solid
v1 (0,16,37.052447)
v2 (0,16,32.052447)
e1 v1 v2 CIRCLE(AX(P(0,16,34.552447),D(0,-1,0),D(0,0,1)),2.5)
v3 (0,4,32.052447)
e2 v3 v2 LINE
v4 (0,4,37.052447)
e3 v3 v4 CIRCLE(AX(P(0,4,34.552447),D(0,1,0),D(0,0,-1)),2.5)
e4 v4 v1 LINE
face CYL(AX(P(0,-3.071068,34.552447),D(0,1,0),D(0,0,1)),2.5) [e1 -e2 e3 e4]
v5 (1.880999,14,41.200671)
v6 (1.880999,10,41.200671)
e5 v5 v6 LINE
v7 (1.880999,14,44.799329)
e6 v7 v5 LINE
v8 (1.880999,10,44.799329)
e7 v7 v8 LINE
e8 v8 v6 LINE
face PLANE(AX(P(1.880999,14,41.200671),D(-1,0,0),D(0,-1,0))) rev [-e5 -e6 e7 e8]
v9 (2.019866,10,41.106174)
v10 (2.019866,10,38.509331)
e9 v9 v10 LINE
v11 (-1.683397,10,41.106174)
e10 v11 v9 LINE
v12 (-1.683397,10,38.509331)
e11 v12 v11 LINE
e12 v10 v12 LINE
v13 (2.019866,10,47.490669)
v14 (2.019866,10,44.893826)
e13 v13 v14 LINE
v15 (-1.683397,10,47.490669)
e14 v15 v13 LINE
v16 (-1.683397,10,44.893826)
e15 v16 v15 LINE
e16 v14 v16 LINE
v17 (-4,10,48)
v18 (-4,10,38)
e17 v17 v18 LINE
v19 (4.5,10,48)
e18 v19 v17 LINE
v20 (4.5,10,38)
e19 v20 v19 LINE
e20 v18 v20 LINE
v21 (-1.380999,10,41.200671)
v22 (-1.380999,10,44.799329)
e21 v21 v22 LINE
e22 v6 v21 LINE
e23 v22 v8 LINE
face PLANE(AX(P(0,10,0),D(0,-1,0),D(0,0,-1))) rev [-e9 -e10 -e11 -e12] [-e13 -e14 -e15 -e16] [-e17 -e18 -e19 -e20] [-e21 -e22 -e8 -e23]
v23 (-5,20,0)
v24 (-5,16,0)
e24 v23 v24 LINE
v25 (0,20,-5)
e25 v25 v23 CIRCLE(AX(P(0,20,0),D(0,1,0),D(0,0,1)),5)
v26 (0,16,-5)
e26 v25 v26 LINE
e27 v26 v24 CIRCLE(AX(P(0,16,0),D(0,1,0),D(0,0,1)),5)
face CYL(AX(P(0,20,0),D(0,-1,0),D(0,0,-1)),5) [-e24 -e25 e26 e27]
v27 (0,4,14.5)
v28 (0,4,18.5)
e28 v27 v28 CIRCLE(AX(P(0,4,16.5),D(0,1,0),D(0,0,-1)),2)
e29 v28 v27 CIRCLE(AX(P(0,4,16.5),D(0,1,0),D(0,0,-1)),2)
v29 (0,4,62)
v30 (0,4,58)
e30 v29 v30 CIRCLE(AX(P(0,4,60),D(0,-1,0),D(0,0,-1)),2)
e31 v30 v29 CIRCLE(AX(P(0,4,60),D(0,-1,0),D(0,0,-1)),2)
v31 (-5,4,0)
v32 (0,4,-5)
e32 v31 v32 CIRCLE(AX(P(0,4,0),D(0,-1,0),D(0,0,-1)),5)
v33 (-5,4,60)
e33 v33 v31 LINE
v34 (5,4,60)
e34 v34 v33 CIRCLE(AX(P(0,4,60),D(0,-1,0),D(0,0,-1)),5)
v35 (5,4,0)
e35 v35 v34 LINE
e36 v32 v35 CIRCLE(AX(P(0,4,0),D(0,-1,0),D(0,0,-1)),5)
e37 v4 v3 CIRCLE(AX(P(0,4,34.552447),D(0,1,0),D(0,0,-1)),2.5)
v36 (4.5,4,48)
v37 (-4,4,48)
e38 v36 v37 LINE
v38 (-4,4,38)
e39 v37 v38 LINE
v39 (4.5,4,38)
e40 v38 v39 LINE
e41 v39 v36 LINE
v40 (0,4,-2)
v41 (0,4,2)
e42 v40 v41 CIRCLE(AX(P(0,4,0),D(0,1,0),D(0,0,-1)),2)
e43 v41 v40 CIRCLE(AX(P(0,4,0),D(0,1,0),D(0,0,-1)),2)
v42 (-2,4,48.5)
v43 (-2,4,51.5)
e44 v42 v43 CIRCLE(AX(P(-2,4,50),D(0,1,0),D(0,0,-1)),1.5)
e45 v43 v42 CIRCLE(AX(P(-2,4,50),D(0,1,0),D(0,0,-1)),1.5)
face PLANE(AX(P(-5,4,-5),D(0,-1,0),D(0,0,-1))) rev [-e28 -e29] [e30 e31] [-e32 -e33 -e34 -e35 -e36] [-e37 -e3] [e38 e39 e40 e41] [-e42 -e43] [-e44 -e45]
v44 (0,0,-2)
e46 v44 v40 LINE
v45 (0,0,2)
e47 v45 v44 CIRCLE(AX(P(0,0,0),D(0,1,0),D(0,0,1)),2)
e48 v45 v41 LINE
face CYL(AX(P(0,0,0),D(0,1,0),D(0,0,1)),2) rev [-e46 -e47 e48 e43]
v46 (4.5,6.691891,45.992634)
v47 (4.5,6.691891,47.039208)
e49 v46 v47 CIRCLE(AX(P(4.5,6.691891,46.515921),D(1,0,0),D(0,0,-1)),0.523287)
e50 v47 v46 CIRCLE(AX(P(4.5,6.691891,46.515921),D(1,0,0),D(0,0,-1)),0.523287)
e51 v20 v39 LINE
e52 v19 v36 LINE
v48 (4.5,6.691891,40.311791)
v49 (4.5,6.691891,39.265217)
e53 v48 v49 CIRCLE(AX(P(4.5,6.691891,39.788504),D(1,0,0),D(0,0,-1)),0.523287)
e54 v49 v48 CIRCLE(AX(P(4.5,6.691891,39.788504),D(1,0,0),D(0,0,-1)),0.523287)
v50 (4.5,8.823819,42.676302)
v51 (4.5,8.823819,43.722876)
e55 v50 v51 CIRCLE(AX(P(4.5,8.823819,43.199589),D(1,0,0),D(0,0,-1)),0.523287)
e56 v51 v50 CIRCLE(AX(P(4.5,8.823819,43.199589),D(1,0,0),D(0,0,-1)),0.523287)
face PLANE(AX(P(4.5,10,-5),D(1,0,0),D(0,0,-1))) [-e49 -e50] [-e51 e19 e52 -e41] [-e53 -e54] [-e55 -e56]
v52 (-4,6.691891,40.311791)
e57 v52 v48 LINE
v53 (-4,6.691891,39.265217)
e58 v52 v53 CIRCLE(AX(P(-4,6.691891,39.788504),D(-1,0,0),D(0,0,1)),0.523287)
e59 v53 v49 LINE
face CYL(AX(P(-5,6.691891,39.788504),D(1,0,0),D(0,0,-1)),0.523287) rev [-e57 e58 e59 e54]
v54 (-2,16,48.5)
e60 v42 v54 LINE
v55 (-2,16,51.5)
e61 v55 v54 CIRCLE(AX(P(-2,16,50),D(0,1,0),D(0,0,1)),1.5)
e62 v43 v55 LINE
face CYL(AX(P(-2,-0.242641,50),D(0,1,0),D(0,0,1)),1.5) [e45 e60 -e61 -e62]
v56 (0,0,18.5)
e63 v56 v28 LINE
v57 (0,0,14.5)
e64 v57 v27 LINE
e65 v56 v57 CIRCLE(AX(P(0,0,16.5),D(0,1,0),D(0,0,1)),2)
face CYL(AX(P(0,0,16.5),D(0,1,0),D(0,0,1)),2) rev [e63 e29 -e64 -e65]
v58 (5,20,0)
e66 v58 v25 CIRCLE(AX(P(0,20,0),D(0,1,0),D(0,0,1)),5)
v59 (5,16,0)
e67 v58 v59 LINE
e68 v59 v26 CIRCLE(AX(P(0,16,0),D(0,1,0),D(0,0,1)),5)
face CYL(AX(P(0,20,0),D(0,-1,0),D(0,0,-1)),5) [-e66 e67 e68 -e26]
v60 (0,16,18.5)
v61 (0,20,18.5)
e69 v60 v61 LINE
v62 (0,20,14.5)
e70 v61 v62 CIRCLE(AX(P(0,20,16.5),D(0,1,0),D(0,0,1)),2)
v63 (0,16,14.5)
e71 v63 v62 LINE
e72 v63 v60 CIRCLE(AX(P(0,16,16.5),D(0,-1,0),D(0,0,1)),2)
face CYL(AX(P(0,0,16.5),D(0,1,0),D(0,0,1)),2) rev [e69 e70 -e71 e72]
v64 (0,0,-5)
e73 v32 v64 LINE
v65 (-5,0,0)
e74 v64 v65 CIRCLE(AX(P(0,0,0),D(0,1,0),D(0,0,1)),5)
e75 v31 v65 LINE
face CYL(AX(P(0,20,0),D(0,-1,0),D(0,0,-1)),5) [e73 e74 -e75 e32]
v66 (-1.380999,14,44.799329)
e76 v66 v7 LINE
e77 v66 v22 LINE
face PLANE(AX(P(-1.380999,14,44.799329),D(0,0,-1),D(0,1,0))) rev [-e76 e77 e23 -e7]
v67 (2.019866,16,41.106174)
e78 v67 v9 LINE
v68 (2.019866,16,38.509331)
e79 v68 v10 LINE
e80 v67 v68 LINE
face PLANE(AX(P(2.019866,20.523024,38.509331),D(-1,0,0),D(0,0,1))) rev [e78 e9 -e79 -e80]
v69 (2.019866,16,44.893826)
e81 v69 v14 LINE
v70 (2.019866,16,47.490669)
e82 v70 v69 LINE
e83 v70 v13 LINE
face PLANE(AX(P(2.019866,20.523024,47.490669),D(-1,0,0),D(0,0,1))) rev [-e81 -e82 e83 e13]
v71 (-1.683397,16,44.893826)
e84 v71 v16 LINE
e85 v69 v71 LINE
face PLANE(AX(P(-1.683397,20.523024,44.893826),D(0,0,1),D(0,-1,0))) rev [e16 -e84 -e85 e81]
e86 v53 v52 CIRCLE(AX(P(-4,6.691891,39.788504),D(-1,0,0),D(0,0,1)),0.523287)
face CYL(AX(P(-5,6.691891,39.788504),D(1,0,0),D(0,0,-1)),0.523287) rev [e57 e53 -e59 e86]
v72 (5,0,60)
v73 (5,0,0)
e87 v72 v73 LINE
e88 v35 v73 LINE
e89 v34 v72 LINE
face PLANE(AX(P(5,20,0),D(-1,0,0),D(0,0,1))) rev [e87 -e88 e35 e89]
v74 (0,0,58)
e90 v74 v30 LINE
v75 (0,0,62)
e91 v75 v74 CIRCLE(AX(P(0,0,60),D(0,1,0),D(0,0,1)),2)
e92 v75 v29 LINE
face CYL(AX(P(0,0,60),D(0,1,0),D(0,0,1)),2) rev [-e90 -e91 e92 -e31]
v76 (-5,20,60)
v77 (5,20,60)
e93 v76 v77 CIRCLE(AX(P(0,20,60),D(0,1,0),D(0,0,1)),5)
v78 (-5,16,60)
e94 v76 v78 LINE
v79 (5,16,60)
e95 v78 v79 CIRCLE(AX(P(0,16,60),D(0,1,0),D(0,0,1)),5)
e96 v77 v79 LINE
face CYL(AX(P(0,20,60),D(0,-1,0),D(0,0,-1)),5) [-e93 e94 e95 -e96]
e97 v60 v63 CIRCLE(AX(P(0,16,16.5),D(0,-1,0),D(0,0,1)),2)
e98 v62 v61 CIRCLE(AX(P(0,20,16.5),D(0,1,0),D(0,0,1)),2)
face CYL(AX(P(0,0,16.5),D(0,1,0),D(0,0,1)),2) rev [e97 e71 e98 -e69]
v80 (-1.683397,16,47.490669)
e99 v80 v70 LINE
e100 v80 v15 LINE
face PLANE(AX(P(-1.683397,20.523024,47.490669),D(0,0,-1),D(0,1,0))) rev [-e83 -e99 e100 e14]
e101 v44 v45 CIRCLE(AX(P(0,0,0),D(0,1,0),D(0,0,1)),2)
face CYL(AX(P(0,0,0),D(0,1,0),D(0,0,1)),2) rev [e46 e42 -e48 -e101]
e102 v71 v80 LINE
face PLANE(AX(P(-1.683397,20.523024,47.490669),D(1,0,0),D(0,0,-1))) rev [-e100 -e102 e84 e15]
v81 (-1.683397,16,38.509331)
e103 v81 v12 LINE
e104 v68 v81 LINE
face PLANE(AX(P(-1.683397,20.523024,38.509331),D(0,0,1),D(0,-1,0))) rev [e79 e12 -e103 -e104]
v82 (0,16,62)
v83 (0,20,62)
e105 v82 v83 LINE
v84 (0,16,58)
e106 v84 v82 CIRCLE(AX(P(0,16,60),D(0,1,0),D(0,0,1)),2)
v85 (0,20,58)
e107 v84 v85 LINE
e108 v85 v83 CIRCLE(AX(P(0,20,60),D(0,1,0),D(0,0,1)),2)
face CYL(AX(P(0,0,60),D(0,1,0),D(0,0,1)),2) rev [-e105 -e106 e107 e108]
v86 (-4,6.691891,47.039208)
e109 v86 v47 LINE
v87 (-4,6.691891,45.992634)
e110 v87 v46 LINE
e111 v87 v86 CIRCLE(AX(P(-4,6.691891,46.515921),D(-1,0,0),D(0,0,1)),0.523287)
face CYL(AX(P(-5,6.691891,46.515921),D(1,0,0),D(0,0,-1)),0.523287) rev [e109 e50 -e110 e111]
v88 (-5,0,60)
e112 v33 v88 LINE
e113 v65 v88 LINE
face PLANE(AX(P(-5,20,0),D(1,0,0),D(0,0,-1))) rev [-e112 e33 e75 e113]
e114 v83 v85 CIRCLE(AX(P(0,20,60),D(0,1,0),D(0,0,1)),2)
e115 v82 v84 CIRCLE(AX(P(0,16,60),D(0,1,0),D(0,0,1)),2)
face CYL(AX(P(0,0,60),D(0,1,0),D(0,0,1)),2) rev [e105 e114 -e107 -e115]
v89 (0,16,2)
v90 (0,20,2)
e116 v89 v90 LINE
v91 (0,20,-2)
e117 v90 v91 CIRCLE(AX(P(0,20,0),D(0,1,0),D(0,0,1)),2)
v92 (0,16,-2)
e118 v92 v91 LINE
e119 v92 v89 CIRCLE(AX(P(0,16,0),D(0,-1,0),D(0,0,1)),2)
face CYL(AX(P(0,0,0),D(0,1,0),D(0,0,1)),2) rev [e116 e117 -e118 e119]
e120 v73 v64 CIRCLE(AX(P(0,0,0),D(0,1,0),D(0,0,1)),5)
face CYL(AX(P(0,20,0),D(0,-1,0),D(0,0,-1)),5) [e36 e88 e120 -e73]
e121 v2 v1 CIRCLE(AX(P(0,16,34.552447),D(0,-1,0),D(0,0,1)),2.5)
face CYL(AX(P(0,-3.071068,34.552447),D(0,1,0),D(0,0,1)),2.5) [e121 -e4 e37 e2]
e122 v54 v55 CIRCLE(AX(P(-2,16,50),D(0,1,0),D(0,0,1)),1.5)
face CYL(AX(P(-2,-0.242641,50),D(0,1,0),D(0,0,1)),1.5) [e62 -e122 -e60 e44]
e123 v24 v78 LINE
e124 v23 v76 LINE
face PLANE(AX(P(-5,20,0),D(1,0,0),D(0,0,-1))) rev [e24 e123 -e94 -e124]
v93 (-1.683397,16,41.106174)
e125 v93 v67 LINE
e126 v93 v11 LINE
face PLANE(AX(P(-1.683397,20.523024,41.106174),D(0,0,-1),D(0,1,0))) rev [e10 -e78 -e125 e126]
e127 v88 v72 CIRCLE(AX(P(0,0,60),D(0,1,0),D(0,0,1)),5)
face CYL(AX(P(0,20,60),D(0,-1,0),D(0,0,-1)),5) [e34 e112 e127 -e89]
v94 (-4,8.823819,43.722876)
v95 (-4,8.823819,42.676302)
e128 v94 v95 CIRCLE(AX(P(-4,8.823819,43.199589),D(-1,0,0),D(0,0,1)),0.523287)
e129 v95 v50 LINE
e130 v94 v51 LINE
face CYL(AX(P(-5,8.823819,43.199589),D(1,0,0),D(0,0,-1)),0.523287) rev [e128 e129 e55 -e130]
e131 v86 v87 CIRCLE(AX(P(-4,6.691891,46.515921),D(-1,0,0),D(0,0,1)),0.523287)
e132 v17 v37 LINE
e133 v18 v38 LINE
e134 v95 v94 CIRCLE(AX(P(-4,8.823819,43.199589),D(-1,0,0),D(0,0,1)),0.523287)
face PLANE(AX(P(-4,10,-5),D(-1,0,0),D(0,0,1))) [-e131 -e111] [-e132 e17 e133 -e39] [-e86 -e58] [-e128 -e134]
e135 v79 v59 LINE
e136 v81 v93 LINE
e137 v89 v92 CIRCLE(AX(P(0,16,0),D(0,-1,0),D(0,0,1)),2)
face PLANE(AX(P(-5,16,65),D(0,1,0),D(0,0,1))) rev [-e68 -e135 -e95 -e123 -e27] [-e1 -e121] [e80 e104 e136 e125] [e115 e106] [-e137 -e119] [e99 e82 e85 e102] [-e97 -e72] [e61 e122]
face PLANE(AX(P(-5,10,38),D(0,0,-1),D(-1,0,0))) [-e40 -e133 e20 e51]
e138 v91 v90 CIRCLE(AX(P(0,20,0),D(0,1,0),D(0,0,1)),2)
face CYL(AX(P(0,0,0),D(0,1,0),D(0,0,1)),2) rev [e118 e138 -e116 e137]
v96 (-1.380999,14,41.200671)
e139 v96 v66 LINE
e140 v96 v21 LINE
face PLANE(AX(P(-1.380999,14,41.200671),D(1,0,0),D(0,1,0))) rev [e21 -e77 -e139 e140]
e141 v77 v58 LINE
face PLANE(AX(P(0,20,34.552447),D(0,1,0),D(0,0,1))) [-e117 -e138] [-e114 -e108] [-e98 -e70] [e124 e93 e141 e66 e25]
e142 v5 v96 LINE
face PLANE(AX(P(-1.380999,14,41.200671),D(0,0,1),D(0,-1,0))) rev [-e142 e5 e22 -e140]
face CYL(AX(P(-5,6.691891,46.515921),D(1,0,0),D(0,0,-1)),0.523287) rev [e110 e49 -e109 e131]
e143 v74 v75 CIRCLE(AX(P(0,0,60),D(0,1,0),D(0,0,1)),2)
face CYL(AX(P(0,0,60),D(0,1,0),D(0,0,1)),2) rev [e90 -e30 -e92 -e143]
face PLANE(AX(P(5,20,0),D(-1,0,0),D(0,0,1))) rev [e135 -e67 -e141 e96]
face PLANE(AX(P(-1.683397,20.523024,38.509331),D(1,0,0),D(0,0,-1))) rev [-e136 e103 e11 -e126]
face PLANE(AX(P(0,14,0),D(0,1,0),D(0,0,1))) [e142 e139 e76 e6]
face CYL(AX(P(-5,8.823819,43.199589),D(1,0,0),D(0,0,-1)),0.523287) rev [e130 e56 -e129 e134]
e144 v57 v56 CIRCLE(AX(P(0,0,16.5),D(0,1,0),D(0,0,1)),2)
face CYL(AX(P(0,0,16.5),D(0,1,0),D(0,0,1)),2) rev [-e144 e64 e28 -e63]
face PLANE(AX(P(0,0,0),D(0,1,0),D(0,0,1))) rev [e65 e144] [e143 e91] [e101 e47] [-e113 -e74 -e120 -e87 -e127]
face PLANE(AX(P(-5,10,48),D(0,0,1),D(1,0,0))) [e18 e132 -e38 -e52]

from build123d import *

# Parameters (mm, degrees)
BOSS_EXTRUDE1_DEPTH     = 20
SKETCH2_R               = 2
CUT_EXTRUDE1_DEPTH      = 69.190908485
CUT_EXTRUDE2_DEPTH      = 69.738635424
CUT_EXTRUDE2_DEPTH_BACK = 69.738635424
SKETCH3_W               = 70
SKETCH3_H               = 12
CUT_EXTRUDE3_DEPTH      = 69.190908485
CUT_EXTRUDE3_DEPTH_BACK = 69.190908485
SKETCH4_R               = 2
SKETCH5_R               = 2.5
BOSS_EXTRUDE2_DEPTH     = 16
SKETCH6_R               = 1.5
BOSS_EXTRUDE3_DEPTH     = 16
BOSS_EXTRUDE4_START     = -16
BOSS_EXTRUDE4_DEPTH     = 6
CUT_EXTRUDE4_DEPTH      = 69.667677986
CUT_EXTRUDE4_DEPTH_BACK = 69.667677986
SKETCH8_R               = 0.52328701
SKETCH9_W               = 3.261997226
SKETCH9_H               = 3.598658034
BOSS_EXTRUDE5_DEPTH     = 4
SKETCH10_W              = 3.703262865
SKETCH10_H              = 2.596843015
BOSS_EXTRUDE6_DEPTH     = 6


with BuildPart() as part:
    # Sketch1 → Boss-Extrude1 (new body)
    with BuildSketch(Plane(origin=(0, 0, 0), x_dir=(1, 0, 0), z_dir=(0, 1, 0))):
        with BuildLine():
            Line((-5, 0), (-5, -60))
            ThreePointArc((-5, -60), (0, -65), (5, -60))
            Line((5, -60), (5, 0))
            ThreePointArc((5, 0), (0, 5), (-5, 0))
        make_face()
    extrude(amount=BOSS_EXTRUDE1_DEPTH)

    # Sketch2 → Cut-Extrude1 (cut, through all)
    with BuildSketch(Plane(origin=(0, 20, 0), x_dir=(1, 0, 0), z_dir=(0, 1, 0))):
        with Locations(Location((0, 0, 0), (0, 0, 270))):
            Circle(SKETCH2_R)
        with Locations(Location((0, -16.5, 0), (0, 0, 270))):
            Circle(SKETCH2_R)
    extrude(amount=-CUT_EXTRUDE1_DEPTH, mode=Mode.SUBTRACT)

    # Sketch3 → Cut-Extrude2 (cut, two sides: drawn at the far end of the back side and taken through both)
    with BuildSketch(Plane(origin=(5, 0, 0), x_dir=(0, 0, -1), z_dir=(1, 0, 0)).offset(-CUT_EXTRUDE2_DEPTH_BACK)):
        with Locations((-30, 10)):
            Rectangle(SKETCH3_W, SKETCH3_H)
    extrude(amount=CUT_EXTRUDE2_DEPTH + CUT_EXTRUDE2_DEPTH_BACK, mode=Mode.SUBTRACT)


with BuildPart() as cut_extrude2_piece_1:
    # of the separate pieces the step leaves, piece 1, a body of its own (cut_extrude2_pieces)
    add(part.part.solids().sort_by_distance((5, 16, 60))[0])


with BuildPart() as cut_extrude2_piece_2:
    # of the separate pieces the step leaves, piece 2, a body of its own (cut_extrude2_pieces)
    add(part.part.solids().sort_by_distance((5, 0, 60))[0])


with BuildPart() as cut_extrude3_tool:
    # Sketch4 → Cut-Extrude3 (new, two sides: drawn at the far end of the back side and taken through both)
    with BuildSketch(Plane(origin=(0, 20, 0), x_dir=(1, 0, 0), z_dir=(0, 1, 0)).offset(-CUT_EXTRUDE3_DEPTH_BACK)):
        with Locations(Location((0, -60, 0), (0, 0, 270))):
            Circle(SKETCH4_R)
    extrude(amount=CUT_EXTRUDE3_DEPTH + CUT_EXTRUDE3_DEPTH_BACK)


with BuildPart() as cut_extrude2_piece_1_1:
    add(cut_extrude2_piece_1.part)

    # Cut-Extrude3: cut by cut_extrude3_tool
    add(cut_extrude3_tool.part, mode=Mode.SUBTRACT)



with BuildPart() as cut_extrude2_piece_2_1:
    add(cut_extrude2_piece_2.part)

    # Cut-Extrude3: cut by cut_extrude3_tool
    add(cut_extrude3_tool.part, mode=Mode.SUBTRACT)


with BuildPart() as cut_extrude2_piece_1_2:
    add(cut_extrude2_piece_1_1.part)

    add(cut_extrude2_piece_2_1.part)  # Boss-Extrude2 merges Cut-Extrude2 piece 2
    # Sketch5 → Boss-Extrude2 (add)
    with BuildSketch(Plane(origin=(0, 20, 0), x_dir=(1, 0, 0), z_dir=(0, 1, 0))):
        with Locations(Location((0, -34.552446897, 0), (0, 0, 270))):
            Circle(SKETCH5_R)
    extrude(amount=-BOSS_EXTRUDE2_DEPTH)

    # Sketch6 → Boss-Extrude3 (add)
    with BuildSketch(Plane(origin=(0, 20, 0), x_dir=(1, 0, 0), z_dir=(0, 1, 0))):
        with Locations(Location((-2, -50, 0), (0, 0, 270))):
            Circle(SKETCH6_R)
    extrude(amount=-BOSS_EXTRUDE3_DEPTH)

    # Sketch7 → Boss-Extrude4 (add)
    with BuildSketch(Plane(origin=(0, 20, 0), x_dir=(1, 0, 0), z_dir=(0, 1, 0)).offset(BOSS_EXTRUDE4_START)):
        Polygon((4.5, -38), (-4, -38), (-4, -48), (4.5, -48), (4.5, -44), align=None)
    extrude(amount=BOSS_EXTRUDE4_DEPTH)

    # Sketch8 → Cut-Extrude4 (cut, two sides: drawn at the far end of the back side and taken through both)
    with BuildSketch(Plane(origin=(4.5, 0, 0), x_dir=(0, 0, -1), z_dir=(1, 0, 0)).offset(-CUT_EXTRUDE4_DEPTH_BACK)):
        with Locations((-39.788503734, 6.691891051)):
            Circle(SKETCH8_R)
        with Locations((-46.515921266, 6.691891051)):
            Circle(SKETCH8_R)
        with Locations((-43.19958868, 8.823819142)):
            Circle(SKETCH8_R)
    extrude(amount=CUT_EXTRUDE4_DEPTH + CUT_EXTRUDE4_DEPTH_BACK, mode=Mode.SUBTRACT)

    # Sketch9 → Boss-Extrude5 (add)
    with BuildSketch(Plane(origin=(0, 10, 0), x_dir=(1, 0, 0), z_dir=(0, 1, 0))):
        with Locations((0.25, -43)):
            Rectangle(SKETCH9_W, SKETCH9_H)
    extrude(amount=BOSS_EXTRUDE5_DEPTH)

    # Sketch10 → Boss-Extrude6 (add)
    with BuildSketch(Plane(origin=(0, 10, 0), x_dir=(1, 0, 0), z_dir=(0, 1, 0))):
        with Locations((0.168234256, -39.807752572)):
            Rectangle(SKETCH10_W, SKETCH10_H)
        with Locations((0.168234256, -46.192247429)):
            Rectangle(SKETCH10_W, SKETCH10_H)
    extrude(amount=BOSS_EXTRUDE6_DEPTH)


solid = cut_extrude2_piece_1_2.part
